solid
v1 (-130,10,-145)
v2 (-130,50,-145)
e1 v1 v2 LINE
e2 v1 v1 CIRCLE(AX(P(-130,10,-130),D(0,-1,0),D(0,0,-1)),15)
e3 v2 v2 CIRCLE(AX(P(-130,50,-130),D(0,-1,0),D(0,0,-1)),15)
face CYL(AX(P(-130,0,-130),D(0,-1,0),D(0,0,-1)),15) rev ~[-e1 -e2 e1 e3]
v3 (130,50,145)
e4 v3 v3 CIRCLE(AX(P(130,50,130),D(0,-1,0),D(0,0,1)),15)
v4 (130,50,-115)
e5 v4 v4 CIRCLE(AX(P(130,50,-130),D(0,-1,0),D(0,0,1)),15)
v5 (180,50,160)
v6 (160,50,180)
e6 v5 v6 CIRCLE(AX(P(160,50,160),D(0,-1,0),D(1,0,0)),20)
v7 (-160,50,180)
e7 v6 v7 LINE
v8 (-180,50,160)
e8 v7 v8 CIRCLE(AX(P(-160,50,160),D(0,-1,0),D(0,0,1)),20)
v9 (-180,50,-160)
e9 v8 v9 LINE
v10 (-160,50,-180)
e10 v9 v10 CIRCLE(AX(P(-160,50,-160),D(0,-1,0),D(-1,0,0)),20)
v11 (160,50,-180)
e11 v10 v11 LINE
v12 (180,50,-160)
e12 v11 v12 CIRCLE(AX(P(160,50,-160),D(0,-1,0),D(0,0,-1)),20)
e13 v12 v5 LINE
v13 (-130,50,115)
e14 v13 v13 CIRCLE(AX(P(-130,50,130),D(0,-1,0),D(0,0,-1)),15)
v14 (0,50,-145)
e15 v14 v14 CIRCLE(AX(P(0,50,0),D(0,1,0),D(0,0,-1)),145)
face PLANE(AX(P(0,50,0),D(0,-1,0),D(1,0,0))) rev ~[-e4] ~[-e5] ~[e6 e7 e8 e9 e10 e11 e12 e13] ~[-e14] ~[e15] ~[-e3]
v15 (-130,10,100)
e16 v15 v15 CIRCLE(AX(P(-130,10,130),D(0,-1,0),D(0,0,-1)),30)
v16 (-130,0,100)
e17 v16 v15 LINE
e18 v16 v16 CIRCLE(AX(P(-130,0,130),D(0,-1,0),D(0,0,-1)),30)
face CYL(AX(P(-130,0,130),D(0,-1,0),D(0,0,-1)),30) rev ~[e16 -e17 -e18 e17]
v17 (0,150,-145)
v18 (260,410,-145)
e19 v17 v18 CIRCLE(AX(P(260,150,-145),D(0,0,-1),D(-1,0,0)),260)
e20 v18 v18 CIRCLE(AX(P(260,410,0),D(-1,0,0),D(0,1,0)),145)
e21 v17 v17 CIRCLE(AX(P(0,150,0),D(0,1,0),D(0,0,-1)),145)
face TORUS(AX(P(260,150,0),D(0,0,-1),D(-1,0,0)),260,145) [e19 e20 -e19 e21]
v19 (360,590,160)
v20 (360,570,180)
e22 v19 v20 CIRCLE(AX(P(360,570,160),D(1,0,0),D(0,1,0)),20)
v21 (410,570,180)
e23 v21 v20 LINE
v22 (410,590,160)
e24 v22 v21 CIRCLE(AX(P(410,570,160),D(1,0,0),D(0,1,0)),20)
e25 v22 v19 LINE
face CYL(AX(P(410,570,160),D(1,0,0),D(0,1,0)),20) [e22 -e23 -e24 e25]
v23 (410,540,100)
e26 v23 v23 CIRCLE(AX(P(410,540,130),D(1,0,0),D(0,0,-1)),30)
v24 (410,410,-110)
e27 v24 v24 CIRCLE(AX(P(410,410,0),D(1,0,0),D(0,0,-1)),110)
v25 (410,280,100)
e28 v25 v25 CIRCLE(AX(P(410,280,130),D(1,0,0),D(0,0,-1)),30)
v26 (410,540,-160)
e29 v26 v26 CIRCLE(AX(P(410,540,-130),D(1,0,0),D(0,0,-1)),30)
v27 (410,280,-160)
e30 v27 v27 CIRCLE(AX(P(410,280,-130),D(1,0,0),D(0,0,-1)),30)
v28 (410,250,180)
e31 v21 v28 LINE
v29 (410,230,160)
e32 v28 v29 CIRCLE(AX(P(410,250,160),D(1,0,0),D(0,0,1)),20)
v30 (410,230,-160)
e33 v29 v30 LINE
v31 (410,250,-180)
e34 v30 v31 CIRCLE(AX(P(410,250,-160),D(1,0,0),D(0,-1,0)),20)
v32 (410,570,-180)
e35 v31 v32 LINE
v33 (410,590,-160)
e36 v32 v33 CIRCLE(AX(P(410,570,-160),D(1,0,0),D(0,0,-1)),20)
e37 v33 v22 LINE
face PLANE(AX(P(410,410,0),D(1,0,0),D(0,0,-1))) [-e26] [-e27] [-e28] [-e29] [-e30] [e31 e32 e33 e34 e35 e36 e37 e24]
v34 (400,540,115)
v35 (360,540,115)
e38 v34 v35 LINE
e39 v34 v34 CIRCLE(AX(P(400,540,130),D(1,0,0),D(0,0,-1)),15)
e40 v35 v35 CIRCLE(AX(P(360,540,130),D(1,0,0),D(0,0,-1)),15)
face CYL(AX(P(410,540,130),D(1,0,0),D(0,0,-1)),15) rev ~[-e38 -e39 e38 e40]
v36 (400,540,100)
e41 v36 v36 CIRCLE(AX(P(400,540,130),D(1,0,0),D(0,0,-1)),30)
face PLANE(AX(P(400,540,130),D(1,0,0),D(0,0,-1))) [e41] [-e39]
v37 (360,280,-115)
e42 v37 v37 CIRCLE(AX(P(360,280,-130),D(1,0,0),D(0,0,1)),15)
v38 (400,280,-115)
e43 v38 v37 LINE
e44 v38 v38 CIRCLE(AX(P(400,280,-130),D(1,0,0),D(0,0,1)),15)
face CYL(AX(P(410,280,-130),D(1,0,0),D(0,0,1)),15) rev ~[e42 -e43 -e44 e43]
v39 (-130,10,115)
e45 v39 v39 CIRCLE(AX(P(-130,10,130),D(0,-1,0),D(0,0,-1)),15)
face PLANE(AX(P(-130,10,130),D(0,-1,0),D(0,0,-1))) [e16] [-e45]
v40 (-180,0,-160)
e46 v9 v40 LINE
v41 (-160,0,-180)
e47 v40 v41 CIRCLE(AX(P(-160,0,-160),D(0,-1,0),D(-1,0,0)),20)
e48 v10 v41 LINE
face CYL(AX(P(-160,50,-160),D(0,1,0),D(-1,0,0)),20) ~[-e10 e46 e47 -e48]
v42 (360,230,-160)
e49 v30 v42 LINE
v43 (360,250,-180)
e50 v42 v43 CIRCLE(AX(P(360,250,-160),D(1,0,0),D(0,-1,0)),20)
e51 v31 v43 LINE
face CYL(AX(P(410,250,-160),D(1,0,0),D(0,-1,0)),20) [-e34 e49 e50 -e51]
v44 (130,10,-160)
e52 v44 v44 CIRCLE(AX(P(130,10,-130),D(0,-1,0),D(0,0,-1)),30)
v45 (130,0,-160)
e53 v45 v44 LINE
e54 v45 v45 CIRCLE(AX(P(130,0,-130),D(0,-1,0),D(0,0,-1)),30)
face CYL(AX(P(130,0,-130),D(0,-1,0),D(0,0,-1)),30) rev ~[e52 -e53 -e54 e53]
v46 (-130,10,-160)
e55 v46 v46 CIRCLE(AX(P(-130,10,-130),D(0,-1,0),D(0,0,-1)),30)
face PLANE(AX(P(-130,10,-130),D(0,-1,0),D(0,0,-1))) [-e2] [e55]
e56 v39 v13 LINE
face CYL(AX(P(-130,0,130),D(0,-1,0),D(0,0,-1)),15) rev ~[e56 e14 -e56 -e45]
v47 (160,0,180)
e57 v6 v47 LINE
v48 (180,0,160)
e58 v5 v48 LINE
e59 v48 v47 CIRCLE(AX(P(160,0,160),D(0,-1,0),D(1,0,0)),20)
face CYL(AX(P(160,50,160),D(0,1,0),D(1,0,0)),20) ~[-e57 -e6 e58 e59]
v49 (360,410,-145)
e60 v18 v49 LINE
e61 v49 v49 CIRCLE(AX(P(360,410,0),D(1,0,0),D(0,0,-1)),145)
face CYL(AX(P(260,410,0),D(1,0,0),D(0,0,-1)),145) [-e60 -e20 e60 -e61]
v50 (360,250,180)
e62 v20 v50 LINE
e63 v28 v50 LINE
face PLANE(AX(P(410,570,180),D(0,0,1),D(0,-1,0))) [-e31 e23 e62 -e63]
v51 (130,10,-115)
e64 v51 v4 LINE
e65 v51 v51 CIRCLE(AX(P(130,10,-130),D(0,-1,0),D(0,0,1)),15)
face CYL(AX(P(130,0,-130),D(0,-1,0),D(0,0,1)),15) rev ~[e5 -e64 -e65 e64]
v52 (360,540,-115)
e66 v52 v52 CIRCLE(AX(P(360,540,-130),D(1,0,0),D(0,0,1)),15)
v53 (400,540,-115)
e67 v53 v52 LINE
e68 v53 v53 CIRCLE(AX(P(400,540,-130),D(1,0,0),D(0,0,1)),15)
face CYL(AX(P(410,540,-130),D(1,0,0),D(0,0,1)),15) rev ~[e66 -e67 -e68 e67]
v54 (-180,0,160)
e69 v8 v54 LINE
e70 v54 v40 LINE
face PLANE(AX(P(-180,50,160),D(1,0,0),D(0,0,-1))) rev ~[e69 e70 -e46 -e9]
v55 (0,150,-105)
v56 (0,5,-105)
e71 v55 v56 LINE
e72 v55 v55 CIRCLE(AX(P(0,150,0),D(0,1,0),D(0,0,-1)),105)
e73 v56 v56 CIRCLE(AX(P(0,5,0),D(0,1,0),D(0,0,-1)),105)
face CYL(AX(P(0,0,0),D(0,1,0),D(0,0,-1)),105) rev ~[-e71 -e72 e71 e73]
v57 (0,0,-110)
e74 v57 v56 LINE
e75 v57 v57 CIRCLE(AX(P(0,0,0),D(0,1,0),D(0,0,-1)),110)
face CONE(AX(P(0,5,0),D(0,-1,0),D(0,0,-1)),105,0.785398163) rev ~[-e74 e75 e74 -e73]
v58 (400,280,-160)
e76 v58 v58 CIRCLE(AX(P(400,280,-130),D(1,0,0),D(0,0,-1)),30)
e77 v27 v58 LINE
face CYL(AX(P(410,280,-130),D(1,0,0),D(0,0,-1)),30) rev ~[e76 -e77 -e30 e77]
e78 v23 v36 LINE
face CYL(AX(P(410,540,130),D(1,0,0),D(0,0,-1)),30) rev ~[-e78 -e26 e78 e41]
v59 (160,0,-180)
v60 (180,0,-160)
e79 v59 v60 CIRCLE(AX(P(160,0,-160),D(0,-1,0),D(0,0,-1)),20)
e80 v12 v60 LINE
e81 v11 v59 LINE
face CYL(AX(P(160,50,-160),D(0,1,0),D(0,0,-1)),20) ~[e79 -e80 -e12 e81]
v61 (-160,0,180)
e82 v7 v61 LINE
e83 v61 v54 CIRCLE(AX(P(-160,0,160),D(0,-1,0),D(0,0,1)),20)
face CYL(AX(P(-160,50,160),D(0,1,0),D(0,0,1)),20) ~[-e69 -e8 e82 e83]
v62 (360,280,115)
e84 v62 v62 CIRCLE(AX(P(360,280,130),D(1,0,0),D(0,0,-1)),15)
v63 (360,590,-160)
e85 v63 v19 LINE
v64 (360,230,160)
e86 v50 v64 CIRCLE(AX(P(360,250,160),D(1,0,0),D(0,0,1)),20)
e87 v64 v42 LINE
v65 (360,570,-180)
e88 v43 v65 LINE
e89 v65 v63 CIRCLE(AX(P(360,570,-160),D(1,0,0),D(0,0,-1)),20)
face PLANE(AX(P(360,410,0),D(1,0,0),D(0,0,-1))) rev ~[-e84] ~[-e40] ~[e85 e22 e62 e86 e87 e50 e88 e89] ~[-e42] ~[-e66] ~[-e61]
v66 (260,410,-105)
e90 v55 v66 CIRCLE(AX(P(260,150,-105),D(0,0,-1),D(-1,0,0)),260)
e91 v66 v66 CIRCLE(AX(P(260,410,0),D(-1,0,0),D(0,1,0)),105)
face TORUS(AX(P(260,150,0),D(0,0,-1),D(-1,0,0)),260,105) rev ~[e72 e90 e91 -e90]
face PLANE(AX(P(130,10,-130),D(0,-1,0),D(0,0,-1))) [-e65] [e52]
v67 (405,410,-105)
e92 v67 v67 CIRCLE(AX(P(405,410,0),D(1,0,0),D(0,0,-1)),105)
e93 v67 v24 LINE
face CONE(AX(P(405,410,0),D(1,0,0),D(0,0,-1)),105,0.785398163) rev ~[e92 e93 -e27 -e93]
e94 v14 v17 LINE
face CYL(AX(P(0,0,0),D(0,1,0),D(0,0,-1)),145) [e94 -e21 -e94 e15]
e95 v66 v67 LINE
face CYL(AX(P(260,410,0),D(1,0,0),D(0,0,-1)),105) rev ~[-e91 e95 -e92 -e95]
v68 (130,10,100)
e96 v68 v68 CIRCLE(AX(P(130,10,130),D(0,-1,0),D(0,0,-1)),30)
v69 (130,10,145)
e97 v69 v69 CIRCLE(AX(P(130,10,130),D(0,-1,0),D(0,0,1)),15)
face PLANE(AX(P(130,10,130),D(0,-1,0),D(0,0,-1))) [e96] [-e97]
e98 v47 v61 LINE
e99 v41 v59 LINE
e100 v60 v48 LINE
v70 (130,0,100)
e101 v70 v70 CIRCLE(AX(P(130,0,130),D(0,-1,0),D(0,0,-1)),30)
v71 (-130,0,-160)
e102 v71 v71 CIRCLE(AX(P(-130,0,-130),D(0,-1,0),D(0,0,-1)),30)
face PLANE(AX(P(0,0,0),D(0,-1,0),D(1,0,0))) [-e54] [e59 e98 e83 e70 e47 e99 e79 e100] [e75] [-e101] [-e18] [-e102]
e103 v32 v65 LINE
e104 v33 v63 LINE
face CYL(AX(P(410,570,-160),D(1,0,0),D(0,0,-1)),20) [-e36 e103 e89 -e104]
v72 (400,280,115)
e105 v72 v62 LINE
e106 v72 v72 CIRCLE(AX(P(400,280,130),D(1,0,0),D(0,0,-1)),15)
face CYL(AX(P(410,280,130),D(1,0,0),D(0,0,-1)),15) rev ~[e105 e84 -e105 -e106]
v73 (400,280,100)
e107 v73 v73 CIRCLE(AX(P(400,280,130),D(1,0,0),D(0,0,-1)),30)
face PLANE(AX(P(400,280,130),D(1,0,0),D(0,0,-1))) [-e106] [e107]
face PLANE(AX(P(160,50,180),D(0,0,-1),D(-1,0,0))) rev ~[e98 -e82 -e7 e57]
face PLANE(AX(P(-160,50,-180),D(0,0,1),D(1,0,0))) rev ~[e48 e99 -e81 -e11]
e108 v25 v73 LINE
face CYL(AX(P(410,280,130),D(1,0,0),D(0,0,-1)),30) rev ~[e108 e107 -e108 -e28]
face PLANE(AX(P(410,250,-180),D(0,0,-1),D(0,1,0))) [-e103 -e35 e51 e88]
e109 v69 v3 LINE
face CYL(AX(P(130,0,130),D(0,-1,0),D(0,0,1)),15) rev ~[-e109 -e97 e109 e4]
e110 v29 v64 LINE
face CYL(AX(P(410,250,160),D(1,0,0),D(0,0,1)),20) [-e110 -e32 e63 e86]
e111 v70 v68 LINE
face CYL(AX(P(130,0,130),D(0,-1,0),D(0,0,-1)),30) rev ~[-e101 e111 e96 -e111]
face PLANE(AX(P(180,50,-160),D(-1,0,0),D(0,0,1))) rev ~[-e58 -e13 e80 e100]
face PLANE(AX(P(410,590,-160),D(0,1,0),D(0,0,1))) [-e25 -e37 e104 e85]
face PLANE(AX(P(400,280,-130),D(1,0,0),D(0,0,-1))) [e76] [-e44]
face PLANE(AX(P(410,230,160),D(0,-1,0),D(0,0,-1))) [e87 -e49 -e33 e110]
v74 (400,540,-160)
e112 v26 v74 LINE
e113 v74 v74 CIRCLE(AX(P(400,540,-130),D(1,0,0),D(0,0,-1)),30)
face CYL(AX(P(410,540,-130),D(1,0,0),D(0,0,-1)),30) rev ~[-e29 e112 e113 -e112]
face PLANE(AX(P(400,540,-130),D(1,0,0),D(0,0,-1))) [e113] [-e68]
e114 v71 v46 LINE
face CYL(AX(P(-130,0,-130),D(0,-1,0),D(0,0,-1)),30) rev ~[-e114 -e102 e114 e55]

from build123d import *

# Parameters (mm, degrees)
ELBOW_SECTION_SKETCH_210_290_R    = 145
ELBOW_SECTION_SKETCH_210_290_R_2  = 105
FLANGE_A_SKETCH_R                 = 105
FLANGE_A_360X360X50_DEPTH         = 50
FLANGE_START                      = -50
FLANGE_B_SKETCH_R                 = 105
FLANGE_B_360X360X50_DEPTH         = 50
EDGE_CHAMFER_5X45_A_SIZE          = 5
EDGE_CHAMFER_5X45_B_SIZE          = 5
FLANGE_B_BOLT_HOLES_SKETCH_R      = 15
FLANGE_B_BOLT_HOLES_30_DEPTH      = 50
FLANGE_B_COUNTERBORES_SKETCH_R    = 30
FLANGE_B_COUNTERBORES_60X10_DEPTH = 10
FLANGE_A_BOLT_HOLES_SKETCH_R      = 15
FLANGE_A_BOLT_HOLES_30_DEPTH      = 50
FLANGE_A_COUNTERBORES_SKETCH_R    = 30
FLANGE_A_COUNTERBORES_60X10_DEPTH = 10


with BuildPart() as part:
    # Elbow Body: sweep along a path in Elbow Path Sketch
    with BuildLine(Plane.XY) as elbow_body_path:
        Line((0, 0), (0, 150))
        ThreePointArc((0, 150), (76.152236891, 333.847763109), (260, 410))
        Line((260, 410), (410, 410))
    # Elbow Section Sketch Ø210-Ø290 → Elbow Body (sweep)
    with BuildSketch(Plane(origin=(410, 0, 0), x_dir=(0, 0, -1), z_dir=(1, 0, 0))):
        with Locations((0, 410)):
            Circle(ELBOW_SECTION_SKETCH_210_290_R)
        with Locations((0, 410)):
            Circle(ELBOW_SECTION_SKETCH_210_290_R_2, mode=Mode.SUBTRACT)
    sweep(path=elbow_body_path.line)

    # Flange A Sketch → Flange A 360x360x50 (add)
    with BuildSketch(Plane(origin=(410, 0, 0), x_dir=(0, 0, -1), z_dir=(1, 0, 0))):
        with BuildLine():
            Line((-160, 230), (160, 230))
            ThreePointArc((160, 230), (174.142135624, 235.857864376), (180, 250))
            Line((180, 250), (180, 570))
            ThreePointArc((180, 570), (174.142135624, 584.142135624), (160, 590))
            Line((160, 590), (-160, 590))
            ThreePointArc((-160, 590), (-174.142135624, 584.142135624), (-180, 570))
            Line((-180, 570), (-180, 250))
            ThreePointArc((-180, 250), (-174.142135624, 235.857864376), (-160, 230))
        make_face()
        with Locations((0, 410)):
            Circle(FLANGE_A_SKETCH_R, mode=Mode.SUBTRACT)
    extrude(amount=-FLANGE_A_360X360X50_DEPTH)

    # Flange B Sketch → Flange B 360x360x50 (add)
    with BuildSketch(Plane.XZ.offset(FLANGE_START)):
        with BuildLine():
            Line((-160, -180), (160, -180))
            ThreePointArc((160, -180), (174.142135624, -174.142135624), (180, -160))
            Line((180, -160), (180, 160))
            ThreePointArc((180, 160), (174.142135624, 174.142135624), (160, 180))
            Line((160, 180), (-160, 180))
            ThreePointArc((-160, 180), (-174.142135624, 174.142135624), (-180, 160))
            Line((-180, 160), (-180, -160))
            ThreePointArc((-180, -160), (-174.142135624, -174.142135624), (-160, -180))
        make_face()
        with Locations(Location((0, 0, 0), (0, 0, 180))):
            Circle(FLANGE_B_SKETCH_R, mode=Mode.SUBTRACT)
    extrude(amount=FLANGE_B_360X360X50_DEPTH)

    # Edge Chamfer 5x45 A
    edge_chamfer_5x45_a_edges = [part.edges().sort_by_distance(p)[0] for p in [
        (0, 0, 105),
    ]]
    chamfer(edge_chamfer_5x45_a_edges, length=EDGE_CHAMFER_5X45_A_SIZE)

    # Edge Chamfer 5x45 B
    edge_chamfer_5x45_b_edges = [part.edges().sort_by_distance(p)[0] for p in [
        (410, 410, 105),
    ]]
    chamfer(edge_chamfer_5x45_b_edges, length=EDGE_CHAMFER_5X45_B_SIZE)

    # Flange B Bolt Holes Sketch → Flange B Bolt Holes Ø30 (cut)
    with BuildSketch(Plane.XZ):
        with Locations(Location((-130, 130, 0), (0, 0, 270))):
            Circle(FLANGE_B_BOLT_HOLES_SKETCH_R)
        with Locations(Location((-130, -130, 0), (0, 0, 270))):
            Circle(FLANGE_B_BOLT_HOLES_SKETCH_R)
        with Locations(Location((130, -130, 0), (0, 0, 90))):
            Circle(FLANGE_B_BOLT_HOLES_SKETCH_R)
        with Locations(Location((130, 130, 0), (0, 0, 90))):
            Circle(FLANGE_B_BOLT_HOLES_SKETCH_R)
    extrude(amount=-FLANGE_B_BOLT_HOLES_30_DEPTH, mode=Mode.SUBTRACT)

    # Flange B Counterbores Sketch → Flange B Counterbores Ø60x10 (cut)
    with BuildSketch(Plane.XZ):
        with Locations(Location((-130, 130, 0), (0, 0, 270))):
            Circle(FLANGE_B_COUNTERBORES_SKETCH_R)
        with Locations(Location((-130, -130, 0), (0, 0, 270))):
            Circle(FLANGE_B_COUNTERBORES_SKETCH_R)
        with Locations(Location((130, -130, 0), (0, 0, 270))):
            Circle(FLANGE_B_COUNTERBORES_SKETCH_R)
        with Locations(Location((130, 130, 0), (0, 0, 270))):
            Circle(FLANGE_B_COUNTERBORES_SKETCH_R)
    extrude(amount=-FLANGE_B_COUNTERBORES_60X10_DEPTH, mode=Mode.SUBTRACT)

    # Flange A Bolt Holes Sketch → Flange A Bolt Holes Ø30 (cut)
    with BuildSketch(Plane(origin=(410, 0, 0), x_dir=(0, 0, -1), z_dir=(1, 0, 0))):
        with Locations((-130, 540)):
            Circle(FLANGE_A_BOLT_HOLES_SKETCH_R)
        with Locations((-130, 280)):
            Circle(FLANGE_A_BOLT_HOLES_SKETCH_R)
        with Locations(Location((130, 280, 0), (0, 0, 180))):
            Circle(FLANGE_A_BOLT_HOLES_SKETCH_R)
        with Locations(Location((130, 540, 0), (0, 0, 180))):
            Circle(FLANGE_A_BOLT_HOLES_SKETCH_R)
    extrude(amount=-FLANGE_A_BOLT_HOLES_30_DEPTH, mode=Mode.SUBTRACT)

    # Flange A Counterbores Sketch → Flange A Counterbores Ø60x10 (cut)
    with BuildSketch(Plane(origin=(410, 0, 0), x_dir=(0, 0, -1), z_dir=(1, 0, 0))):
        with Locations((-130, 540)):
            Circle(FLANGE_A_COUNTERBORES_SKETCH_R)
        with Locations((130, 540)):
            Circle(FLANGE_A_COUNTERBORES_SKETCH_R)
        with Locations((-130, 280)):
            Circle(FLANGE_A_COUNTERBORES_SKETCH_R)
        with Locations((130, 280)):
            Circle(FLANGE_A_COUNTERBORES_SKETCH_R)
    extrude(amount=-FLANGE_A_COUNTERBORES_60X10_DEPTH, mode=Mode.SUBTRACT)


solid = part.part
